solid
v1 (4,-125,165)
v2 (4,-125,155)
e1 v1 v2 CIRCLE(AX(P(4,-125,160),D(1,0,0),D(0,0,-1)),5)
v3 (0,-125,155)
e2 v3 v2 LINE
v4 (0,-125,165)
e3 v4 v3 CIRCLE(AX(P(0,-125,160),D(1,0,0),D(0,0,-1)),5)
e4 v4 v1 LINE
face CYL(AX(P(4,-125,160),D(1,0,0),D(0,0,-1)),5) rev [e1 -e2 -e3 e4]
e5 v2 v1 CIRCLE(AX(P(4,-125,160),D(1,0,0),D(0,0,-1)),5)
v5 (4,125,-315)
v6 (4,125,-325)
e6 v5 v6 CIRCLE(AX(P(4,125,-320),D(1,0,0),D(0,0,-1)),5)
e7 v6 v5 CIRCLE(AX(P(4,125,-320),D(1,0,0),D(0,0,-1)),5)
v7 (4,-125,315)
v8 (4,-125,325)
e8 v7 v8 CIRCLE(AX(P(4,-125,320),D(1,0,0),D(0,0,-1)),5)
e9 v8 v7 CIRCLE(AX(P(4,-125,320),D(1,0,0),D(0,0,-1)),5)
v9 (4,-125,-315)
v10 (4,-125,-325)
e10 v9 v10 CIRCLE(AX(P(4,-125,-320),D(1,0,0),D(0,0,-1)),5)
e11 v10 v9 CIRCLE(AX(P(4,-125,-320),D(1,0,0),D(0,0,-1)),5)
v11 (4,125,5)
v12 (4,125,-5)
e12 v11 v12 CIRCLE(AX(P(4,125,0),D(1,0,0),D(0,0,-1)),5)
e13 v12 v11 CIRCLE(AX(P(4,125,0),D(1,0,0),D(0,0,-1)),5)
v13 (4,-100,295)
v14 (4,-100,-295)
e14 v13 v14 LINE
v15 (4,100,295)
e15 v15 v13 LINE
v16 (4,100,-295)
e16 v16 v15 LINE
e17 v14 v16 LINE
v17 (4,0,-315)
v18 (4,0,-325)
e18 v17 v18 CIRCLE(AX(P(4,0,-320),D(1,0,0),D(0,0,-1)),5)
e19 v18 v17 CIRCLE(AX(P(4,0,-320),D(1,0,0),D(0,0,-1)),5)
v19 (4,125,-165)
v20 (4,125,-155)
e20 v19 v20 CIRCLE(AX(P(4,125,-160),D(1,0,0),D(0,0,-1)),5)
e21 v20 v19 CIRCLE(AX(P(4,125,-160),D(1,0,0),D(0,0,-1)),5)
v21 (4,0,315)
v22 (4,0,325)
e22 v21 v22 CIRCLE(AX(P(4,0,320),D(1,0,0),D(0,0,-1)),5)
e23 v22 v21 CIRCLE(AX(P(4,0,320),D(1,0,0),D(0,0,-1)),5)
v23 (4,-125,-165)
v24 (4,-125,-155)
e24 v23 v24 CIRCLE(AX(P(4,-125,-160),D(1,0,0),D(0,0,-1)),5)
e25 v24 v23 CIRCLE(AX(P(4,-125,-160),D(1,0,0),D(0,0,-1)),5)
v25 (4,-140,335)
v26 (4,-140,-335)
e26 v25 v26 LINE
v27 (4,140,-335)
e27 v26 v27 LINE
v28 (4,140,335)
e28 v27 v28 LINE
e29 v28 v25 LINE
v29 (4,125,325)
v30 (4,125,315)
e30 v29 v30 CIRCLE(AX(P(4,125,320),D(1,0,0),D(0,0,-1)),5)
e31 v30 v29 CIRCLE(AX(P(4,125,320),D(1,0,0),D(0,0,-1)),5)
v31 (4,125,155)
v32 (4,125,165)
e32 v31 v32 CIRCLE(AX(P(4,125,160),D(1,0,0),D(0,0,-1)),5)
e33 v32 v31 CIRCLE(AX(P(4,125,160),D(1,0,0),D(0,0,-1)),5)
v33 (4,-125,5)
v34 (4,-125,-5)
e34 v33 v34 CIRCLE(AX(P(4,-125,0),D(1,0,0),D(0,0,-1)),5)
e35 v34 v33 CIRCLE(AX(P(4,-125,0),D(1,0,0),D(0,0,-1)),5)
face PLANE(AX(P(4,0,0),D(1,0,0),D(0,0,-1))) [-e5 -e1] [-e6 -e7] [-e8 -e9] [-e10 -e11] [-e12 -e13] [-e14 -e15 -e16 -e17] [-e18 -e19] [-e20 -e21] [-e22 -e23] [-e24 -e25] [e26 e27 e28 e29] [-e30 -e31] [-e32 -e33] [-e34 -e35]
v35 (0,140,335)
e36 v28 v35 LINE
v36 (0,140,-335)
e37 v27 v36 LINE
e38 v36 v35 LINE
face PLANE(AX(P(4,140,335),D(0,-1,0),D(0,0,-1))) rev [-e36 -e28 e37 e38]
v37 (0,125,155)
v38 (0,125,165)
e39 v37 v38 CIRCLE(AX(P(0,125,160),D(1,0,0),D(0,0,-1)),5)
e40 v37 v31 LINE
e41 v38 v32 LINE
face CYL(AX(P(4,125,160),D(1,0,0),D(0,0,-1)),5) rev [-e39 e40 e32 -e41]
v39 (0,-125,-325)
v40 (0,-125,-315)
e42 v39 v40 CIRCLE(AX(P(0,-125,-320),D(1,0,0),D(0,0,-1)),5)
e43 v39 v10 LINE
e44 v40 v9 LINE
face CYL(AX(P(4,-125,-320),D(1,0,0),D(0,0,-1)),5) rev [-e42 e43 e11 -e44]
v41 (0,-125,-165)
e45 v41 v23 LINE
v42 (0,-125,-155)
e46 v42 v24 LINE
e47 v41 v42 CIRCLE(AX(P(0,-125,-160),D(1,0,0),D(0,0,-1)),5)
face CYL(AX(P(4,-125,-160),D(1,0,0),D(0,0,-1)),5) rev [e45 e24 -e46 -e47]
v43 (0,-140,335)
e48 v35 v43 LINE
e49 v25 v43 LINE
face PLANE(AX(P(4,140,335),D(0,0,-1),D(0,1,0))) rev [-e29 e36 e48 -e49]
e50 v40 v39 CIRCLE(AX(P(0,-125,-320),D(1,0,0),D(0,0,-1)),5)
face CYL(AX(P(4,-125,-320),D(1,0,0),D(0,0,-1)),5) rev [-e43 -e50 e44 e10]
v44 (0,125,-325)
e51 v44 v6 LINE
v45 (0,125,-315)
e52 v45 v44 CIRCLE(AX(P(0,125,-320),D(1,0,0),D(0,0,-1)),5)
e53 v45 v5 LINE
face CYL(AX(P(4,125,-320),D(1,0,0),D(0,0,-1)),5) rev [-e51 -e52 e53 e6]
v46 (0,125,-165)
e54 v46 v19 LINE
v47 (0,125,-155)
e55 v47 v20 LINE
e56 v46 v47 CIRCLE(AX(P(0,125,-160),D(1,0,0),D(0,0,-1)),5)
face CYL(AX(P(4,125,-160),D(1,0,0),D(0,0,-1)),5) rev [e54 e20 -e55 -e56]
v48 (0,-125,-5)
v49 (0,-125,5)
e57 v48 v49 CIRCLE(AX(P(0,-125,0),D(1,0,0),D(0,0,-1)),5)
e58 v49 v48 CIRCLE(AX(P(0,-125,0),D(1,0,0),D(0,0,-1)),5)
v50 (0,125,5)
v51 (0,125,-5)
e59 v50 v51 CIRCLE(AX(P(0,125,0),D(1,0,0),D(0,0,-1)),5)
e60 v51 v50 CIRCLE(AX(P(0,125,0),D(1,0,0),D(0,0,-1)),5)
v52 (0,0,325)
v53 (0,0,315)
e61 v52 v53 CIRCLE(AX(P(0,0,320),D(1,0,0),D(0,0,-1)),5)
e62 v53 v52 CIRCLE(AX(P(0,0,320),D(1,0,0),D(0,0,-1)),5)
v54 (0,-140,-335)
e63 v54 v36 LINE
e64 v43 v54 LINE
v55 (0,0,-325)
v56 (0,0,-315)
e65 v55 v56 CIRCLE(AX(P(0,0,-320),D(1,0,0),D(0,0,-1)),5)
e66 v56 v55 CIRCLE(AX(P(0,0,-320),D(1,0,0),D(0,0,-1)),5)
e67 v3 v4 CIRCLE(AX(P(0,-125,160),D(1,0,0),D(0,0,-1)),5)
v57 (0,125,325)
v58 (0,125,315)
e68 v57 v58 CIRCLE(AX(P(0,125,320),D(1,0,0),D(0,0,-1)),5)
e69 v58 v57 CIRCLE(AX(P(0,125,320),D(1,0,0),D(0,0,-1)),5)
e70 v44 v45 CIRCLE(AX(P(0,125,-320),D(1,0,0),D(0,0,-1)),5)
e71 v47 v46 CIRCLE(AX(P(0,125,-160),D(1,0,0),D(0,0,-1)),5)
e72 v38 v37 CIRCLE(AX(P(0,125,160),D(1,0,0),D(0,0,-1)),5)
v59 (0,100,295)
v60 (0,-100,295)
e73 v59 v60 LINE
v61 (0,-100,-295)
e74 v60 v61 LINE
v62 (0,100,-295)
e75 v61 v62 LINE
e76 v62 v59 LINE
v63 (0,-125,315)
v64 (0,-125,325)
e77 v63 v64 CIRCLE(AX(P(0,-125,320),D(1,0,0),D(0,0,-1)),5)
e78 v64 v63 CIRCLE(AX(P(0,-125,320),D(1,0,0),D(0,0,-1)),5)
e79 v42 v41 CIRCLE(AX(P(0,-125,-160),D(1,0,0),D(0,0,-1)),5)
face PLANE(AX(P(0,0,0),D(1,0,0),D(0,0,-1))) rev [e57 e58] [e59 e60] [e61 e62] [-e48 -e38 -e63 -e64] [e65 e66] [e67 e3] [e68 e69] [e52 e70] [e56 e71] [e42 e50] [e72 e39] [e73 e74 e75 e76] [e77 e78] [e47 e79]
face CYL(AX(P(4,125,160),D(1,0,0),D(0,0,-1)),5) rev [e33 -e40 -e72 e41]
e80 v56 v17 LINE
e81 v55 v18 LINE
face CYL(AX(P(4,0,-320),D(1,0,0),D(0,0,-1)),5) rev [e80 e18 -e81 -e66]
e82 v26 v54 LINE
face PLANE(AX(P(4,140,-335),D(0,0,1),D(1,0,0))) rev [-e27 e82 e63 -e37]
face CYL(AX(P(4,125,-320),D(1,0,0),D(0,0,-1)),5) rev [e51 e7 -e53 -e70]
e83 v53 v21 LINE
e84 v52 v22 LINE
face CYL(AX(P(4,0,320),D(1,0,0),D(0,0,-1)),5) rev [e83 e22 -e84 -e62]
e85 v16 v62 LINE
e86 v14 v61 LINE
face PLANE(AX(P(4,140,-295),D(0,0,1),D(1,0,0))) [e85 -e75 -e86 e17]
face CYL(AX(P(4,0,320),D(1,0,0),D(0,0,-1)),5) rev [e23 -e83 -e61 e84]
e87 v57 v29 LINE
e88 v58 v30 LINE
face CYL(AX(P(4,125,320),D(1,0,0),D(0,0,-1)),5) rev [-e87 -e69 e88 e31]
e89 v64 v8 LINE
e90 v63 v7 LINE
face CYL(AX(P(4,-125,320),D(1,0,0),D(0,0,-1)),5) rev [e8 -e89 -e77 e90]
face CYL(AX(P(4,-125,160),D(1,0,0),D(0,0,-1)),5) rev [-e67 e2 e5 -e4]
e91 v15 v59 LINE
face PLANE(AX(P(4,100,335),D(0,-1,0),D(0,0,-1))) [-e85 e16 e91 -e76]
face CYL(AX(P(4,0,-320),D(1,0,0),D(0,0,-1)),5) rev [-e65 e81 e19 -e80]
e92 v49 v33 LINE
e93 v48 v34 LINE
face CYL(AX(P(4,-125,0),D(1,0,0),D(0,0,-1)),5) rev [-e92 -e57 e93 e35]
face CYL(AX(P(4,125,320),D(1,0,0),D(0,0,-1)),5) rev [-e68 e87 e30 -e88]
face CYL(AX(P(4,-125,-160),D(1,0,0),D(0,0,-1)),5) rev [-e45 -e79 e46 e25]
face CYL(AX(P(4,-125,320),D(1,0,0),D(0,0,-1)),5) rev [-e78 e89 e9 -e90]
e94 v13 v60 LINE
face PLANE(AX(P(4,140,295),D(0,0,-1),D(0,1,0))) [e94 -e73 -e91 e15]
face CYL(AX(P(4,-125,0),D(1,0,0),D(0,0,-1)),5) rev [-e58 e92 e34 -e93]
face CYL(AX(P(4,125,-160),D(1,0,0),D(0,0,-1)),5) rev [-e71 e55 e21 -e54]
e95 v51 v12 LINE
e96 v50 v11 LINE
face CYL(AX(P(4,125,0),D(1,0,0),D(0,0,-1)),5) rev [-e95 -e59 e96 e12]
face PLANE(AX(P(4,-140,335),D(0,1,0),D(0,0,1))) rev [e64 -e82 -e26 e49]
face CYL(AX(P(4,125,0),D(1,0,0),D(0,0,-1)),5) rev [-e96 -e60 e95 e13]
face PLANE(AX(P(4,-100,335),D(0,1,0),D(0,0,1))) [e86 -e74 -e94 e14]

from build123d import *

# Parameters (mm, degrees)
SKETCH_1_W                  = 670
SKETCH_1_H                  = 280
SKETCH_1_W_2                = 590
SKETCH_1_H_2                = 200
EXTRUDE_1_DEPTH             = 4
HOLE_WIZARD_10_0_10_1_D     = 10
PATTERN_LINEAR_1_COUNT      = 5
PATTERN_LINEAR_1_PITCH      = 160
PATTERN_LINEAR_1_COUNT_DIR2 = 3
PATTERN_LINEAR_1_PITCH_DIR2 = 125


with BuildPart() as part:
    # 草图1 → 拉伸-薄壁1 (new body)
    with BuildSketch(Plane(origin=(0, 0, 0), x_dir=(0, 0, -1), z_dir=(1, 0, 0))):
        Rectangle(SKETCH_1_W, SKETCH_1_H)
        Rectangle(SKETCH_1_W_2, SKETCH_1_H_2, mode=Mode.SUBTRACT)
    extrude(amount=EXTRUDE_1_DEPTH)

    # Ø10.0 (10) 直径孔1 (through all)
    with Locations(Plane(origin=(4, 0, 0), x_dir=(0, 0, -1), z_dir=(1, 0, 0))):
        with Locations((-320, 125)):
            hole_wizard_10_0_10_1 = Hole(HOLE_WIZARD_10_0_10_1_D / 2)

    # 阵列(线性)1: Hole Wizard 10.0 _10_ _1 5 × 3, 3 skipped
    with Locations(*[(0, -j * PATTERN_LINEAR_1_PITCH_DIR2, -i * PATTERN_LINEAR_1_PITCH) for i in range(PATTERN_LINEAR_1_COUNT) for j in range(PATTERN_LINEAR_1_COUNT_DIR2) if (i, j) not in ((0, 0), (1, 1), (2, 1), (3, 1))]):
        add(hole_wizard_10_0_10_1, mode=Mode.SUBTRACT)


solid = part.part
